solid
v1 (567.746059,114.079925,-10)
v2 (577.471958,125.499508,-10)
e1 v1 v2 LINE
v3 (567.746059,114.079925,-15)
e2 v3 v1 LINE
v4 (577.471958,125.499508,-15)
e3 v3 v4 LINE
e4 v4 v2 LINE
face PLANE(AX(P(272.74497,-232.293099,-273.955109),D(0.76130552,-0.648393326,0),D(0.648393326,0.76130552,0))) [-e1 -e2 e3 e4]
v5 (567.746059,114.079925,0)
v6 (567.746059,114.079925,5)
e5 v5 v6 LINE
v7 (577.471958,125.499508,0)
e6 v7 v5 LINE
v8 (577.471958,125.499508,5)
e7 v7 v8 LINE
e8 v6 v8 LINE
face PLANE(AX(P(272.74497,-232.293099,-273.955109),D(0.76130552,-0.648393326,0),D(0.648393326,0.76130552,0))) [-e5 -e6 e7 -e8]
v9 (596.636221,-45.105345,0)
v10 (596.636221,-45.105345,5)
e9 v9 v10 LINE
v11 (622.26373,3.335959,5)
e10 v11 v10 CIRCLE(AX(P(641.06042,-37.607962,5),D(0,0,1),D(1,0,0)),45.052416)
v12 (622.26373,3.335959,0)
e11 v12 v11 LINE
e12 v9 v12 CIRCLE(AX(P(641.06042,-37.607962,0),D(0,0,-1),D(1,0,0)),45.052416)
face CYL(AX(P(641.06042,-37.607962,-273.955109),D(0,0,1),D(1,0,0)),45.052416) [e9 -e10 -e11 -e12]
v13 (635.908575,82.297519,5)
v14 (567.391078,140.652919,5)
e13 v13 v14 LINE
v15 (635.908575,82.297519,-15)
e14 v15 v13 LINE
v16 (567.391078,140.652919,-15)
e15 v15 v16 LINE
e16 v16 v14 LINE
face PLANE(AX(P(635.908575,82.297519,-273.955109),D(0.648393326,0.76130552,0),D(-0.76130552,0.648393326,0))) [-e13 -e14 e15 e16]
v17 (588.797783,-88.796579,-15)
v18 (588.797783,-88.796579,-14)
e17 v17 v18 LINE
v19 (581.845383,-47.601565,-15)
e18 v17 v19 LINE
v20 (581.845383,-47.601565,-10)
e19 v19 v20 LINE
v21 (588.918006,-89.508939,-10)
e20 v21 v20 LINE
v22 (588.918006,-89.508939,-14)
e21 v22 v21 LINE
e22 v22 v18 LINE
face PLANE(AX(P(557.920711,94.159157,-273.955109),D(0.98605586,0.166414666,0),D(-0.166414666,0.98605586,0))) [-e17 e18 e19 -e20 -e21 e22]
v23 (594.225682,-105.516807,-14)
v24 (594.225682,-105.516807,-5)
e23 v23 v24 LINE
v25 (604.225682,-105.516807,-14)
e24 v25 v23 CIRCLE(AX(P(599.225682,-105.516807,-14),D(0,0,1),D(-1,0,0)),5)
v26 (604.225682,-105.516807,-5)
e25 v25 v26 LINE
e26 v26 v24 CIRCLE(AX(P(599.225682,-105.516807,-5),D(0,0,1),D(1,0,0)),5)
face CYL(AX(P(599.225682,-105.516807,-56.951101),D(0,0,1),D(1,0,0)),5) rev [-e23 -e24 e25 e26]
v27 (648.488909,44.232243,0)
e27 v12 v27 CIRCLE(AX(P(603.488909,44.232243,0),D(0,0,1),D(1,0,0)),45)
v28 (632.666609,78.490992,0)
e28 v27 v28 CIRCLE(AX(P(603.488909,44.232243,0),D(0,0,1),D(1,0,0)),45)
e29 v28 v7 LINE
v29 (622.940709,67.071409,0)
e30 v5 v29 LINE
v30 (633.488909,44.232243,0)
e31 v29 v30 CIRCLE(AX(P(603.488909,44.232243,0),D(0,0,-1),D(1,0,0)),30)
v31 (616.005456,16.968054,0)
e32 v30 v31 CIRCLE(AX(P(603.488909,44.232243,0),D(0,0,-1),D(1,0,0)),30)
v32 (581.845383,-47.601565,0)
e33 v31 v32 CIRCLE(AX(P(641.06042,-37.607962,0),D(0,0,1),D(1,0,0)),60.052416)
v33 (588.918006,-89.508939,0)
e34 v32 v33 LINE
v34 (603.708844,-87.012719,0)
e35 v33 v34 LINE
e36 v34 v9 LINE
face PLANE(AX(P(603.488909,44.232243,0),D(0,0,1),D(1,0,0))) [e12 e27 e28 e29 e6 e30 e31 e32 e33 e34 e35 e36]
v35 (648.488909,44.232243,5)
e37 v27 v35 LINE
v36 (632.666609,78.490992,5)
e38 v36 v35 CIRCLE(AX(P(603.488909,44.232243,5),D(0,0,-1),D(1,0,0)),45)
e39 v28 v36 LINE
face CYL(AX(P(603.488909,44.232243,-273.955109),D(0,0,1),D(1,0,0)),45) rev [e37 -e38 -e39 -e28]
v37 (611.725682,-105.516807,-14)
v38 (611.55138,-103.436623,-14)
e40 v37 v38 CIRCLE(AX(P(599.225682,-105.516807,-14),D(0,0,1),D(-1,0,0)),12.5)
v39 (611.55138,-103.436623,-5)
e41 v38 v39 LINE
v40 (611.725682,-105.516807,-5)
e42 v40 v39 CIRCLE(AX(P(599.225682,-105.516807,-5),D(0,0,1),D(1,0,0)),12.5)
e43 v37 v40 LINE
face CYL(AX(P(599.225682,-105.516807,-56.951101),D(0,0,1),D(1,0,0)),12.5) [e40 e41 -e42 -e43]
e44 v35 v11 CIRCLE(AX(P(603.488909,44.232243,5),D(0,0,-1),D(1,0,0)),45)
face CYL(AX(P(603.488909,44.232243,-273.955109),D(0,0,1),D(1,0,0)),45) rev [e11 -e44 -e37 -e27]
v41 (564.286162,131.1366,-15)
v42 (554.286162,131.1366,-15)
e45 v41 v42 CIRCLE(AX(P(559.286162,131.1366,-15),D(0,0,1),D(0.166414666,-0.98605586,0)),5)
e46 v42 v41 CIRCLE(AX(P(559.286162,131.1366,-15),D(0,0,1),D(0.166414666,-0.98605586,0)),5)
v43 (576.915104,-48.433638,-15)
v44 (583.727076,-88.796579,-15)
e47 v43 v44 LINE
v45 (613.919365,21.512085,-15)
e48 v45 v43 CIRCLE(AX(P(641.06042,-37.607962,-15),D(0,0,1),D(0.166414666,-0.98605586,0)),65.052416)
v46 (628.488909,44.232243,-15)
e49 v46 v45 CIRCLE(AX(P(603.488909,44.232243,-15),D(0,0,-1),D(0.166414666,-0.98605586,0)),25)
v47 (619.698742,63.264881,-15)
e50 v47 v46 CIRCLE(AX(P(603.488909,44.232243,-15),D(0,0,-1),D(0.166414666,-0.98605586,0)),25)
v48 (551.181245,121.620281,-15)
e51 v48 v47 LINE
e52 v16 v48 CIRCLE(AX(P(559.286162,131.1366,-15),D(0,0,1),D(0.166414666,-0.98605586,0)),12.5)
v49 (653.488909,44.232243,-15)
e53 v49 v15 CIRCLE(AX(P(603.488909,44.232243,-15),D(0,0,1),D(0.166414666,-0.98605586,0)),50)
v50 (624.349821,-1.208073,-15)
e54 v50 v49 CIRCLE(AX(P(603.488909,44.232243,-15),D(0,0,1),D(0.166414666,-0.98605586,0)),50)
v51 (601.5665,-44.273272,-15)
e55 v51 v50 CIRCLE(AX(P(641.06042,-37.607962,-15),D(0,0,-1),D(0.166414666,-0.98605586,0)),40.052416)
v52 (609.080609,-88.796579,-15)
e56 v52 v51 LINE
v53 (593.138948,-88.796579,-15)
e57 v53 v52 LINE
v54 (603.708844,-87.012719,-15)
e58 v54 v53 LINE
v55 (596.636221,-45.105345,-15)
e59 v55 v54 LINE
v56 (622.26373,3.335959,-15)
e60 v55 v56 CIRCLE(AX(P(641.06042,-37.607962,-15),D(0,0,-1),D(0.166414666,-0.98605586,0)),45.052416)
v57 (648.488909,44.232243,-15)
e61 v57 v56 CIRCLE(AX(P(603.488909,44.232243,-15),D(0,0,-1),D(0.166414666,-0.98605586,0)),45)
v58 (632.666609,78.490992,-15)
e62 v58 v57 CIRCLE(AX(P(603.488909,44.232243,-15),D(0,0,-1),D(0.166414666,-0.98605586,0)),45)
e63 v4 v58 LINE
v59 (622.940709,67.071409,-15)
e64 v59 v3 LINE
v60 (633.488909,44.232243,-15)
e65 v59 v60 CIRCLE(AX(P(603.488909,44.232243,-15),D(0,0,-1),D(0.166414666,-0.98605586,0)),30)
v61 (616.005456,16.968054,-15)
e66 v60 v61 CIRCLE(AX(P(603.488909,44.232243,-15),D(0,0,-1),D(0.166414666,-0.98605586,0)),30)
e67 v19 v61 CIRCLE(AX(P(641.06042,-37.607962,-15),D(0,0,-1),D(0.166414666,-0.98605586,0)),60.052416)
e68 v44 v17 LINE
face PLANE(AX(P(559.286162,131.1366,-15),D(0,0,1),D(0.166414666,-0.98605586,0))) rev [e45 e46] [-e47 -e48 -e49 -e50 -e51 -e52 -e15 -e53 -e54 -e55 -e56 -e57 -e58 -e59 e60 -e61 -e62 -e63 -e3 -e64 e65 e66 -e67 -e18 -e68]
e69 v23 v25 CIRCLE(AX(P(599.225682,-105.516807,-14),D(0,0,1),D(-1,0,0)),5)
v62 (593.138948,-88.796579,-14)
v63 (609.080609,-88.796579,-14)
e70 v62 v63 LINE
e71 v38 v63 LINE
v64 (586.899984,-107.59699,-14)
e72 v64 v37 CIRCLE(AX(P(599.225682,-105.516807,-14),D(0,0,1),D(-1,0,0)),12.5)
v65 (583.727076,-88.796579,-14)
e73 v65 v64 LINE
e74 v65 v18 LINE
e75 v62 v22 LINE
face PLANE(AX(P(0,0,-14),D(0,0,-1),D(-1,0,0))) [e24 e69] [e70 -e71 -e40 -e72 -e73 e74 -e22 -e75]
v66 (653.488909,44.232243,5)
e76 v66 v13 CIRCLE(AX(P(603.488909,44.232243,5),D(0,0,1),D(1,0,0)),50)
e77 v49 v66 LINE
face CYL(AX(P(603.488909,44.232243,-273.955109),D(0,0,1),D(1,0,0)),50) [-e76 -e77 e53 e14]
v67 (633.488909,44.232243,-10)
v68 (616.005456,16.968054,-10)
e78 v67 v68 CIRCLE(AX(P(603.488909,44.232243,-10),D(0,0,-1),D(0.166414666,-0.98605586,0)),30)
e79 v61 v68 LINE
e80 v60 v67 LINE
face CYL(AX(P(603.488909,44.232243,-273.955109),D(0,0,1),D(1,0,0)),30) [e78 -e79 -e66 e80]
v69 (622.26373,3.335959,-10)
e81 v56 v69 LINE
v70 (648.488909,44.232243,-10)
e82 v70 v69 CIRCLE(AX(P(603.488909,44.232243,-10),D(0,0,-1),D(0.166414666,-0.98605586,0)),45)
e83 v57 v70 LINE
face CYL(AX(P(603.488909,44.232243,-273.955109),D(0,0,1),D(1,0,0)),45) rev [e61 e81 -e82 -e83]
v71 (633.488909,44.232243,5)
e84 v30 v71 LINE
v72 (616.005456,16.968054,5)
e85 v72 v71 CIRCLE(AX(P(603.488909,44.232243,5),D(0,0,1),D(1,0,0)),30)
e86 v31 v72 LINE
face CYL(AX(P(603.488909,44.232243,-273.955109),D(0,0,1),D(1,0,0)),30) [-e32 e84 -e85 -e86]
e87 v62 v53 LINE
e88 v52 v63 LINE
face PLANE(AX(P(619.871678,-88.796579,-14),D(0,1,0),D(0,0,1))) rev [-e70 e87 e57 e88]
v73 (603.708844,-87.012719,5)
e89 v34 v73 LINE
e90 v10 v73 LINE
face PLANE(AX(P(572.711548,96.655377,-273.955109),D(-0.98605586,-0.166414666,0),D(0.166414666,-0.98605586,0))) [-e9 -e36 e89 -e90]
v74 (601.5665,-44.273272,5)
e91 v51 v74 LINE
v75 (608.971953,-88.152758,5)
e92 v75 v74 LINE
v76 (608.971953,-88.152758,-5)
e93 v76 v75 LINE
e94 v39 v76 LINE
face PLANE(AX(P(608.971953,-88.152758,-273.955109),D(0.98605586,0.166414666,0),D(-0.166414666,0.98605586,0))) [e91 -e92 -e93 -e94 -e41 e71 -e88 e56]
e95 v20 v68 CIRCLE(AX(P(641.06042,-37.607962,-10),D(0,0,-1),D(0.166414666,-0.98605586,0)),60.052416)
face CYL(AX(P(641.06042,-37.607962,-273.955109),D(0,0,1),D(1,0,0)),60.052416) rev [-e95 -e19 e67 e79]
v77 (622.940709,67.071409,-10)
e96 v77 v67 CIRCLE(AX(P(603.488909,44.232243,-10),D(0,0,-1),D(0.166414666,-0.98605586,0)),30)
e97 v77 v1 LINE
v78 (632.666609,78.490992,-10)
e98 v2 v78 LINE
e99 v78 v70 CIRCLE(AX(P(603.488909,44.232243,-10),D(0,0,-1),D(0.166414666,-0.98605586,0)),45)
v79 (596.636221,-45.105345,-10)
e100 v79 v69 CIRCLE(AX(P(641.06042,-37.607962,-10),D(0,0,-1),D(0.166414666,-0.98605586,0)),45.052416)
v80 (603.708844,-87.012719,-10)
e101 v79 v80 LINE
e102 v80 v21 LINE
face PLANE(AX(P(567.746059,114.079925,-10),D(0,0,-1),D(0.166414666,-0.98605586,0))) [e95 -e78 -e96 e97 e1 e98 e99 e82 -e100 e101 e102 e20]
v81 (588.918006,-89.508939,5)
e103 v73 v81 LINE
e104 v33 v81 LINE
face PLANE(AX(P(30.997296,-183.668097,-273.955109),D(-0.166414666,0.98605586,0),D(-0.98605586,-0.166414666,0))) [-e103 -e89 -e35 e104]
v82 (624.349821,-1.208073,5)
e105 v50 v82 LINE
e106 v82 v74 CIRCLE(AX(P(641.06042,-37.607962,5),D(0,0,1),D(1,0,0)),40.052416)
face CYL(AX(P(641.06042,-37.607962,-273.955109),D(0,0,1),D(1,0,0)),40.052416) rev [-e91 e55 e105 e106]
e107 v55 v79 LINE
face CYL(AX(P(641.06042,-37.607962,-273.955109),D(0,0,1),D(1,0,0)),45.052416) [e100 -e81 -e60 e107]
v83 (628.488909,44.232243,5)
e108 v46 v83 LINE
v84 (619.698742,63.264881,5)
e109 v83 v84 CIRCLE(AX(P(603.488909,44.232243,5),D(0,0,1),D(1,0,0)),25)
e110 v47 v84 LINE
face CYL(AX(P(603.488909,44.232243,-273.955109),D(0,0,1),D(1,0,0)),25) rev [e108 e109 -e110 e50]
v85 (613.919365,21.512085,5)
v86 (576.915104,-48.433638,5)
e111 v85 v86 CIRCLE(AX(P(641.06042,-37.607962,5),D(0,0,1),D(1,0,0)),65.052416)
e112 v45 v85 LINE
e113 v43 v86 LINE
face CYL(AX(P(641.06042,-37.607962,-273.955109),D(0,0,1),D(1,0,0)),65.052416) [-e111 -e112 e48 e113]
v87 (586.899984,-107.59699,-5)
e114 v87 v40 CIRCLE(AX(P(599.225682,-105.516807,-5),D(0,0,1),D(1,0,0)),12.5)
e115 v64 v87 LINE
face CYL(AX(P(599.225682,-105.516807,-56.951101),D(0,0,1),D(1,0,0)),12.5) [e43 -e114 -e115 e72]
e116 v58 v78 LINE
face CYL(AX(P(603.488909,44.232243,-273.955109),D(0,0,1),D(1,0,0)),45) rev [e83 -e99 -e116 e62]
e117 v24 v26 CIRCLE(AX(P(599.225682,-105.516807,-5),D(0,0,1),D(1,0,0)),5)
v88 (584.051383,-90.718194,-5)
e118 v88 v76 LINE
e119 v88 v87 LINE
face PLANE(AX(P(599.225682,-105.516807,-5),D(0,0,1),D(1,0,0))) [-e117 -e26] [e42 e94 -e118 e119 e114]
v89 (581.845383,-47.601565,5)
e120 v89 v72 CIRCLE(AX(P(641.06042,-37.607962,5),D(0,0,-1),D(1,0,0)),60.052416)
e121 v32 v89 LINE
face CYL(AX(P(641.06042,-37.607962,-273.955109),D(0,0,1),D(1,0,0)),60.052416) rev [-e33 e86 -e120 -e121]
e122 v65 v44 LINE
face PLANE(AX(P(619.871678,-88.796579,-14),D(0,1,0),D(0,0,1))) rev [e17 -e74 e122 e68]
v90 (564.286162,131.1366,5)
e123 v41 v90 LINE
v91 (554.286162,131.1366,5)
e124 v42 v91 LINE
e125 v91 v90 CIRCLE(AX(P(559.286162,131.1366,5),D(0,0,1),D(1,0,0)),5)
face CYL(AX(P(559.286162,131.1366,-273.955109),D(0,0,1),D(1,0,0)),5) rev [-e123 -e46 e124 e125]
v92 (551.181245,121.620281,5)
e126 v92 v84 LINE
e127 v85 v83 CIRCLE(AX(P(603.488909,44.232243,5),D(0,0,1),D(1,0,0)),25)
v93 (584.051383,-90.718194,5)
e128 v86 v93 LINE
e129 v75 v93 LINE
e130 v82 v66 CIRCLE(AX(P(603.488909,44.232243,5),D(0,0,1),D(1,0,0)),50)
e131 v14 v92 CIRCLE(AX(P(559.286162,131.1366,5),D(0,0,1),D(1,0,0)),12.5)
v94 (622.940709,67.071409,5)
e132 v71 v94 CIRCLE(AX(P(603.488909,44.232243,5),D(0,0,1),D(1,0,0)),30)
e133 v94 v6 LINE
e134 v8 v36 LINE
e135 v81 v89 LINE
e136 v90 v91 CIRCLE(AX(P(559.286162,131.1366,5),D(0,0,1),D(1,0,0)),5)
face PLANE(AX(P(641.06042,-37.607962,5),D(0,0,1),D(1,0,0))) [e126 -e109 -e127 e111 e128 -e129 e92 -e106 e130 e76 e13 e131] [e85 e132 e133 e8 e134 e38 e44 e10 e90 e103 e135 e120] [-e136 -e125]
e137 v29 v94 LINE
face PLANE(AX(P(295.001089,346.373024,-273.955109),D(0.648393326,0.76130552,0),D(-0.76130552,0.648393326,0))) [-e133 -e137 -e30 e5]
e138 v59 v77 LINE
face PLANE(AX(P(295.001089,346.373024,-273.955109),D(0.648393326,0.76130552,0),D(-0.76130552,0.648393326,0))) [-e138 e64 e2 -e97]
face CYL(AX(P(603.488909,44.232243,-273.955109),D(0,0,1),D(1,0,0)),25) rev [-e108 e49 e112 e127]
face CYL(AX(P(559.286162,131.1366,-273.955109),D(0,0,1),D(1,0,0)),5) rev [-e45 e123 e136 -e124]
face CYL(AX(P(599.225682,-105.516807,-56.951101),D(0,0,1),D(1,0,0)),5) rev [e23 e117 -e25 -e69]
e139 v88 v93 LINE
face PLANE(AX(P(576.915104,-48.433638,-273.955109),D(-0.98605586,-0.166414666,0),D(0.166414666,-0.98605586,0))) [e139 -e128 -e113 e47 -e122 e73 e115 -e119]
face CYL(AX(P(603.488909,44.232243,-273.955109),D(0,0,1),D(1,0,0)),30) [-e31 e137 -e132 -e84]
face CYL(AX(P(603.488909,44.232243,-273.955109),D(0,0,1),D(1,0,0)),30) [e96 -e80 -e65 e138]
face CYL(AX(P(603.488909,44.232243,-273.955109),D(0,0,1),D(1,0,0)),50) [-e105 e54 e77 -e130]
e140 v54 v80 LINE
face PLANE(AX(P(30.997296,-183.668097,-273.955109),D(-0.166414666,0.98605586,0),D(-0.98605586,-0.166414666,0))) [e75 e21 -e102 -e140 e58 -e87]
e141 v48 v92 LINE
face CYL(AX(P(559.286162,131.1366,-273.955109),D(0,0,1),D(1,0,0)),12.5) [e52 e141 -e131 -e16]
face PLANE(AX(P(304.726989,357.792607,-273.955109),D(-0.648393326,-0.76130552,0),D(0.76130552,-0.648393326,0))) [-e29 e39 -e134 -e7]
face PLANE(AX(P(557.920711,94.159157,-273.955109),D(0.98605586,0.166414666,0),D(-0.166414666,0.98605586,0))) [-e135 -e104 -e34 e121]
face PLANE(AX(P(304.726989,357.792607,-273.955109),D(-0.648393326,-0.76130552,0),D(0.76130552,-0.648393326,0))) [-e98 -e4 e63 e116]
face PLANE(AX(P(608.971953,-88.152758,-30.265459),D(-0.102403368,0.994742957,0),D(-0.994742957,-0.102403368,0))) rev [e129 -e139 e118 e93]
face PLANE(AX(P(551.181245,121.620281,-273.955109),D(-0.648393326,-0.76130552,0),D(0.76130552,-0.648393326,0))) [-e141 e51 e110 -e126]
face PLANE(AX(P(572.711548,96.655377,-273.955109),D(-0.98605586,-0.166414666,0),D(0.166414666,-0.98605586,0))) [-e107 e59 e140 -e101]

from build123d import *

# Parameters (mm, degrees)
BOSS_EXTRUDE1_DEPTH = 10
BOSS_EXTRUDE2_START = -20
BOSS_EXTRUDE2_DEPTH = 20
BOSS_EXTRUDE3_DEPTH = 10
SKETCH6_W           = 47.967212756
SKETCH6_H           = 31.917124467
CUT_EXTRUDE1_DEPTH  = 1
CUT_EXTRUDE2_DEPTH  = 10


with BuildPart() as part:
    # Sketch2 → Boss-Extrude1 (new body)
    with BuildSketch(Plane.XY):
        with BuildLine():
            Line((567.746058529, 114.079925051), (622.940708708, 67.071408889))
            ThreePointArc((622.940708708, 67.071408889), (633.205576943, 40.118894124), (616.005456238, 16.96805354))
            ThreePointArc((616.005456238, 16.96805354), (587.978717163, -9.525484834), (581.845382902, -47.601565115))
            Line((581.845382902, -47.601565115), (588.918006227, -89.508939159))
            Line((588.918006227, -89.508939159), (603.708844125, -87.012719162))
            Line((603.708844125, -87.012719162), (596.6362208, -45.105345118))
            ThreePointArc((596.6362208, -45.105345118), (601.237559856, -16.539976295), (622.263729898, 3.335958661))
            ThreePointArc((622.263729898, 3.335958661), (648.063910956, 38.062219537), (632.666608603, 78.490991685))
            Line((632.666608603, 78.490991685), (577.471958425, 125.499507846))
            Line((577.471958425, 125.499507846), (567.746058529, 114.079925051))
        make_face()
    extrude(amount=-BOSS_EXTRUDE1_DEPTH)

    # Sketch3 → Boss-Extrude2 (add)
    with BuildSketch(Plane.XY.offset(5).offset(BOSS_EXTRUDE2_START)):
        with BuildLine():
            Line((608.971952758, -88.152757549), (601.566500099, -44.273271785))
            ThreePointArc((601.566500099, -44.273271785), (605.657174086, -18.878140116), (624.349821118, -1.208072965))
            ThreePointArc((624.349821118, -1.208072965), (653.01668896, 37.376661342), (635.908575235, 82.297519283))
            Line((635.908575235, 82.297519283), (567.391078462, 140.652918656))
            ThreePointArc((567.391078462, 140.652918656), (549.769842886, 139.241516239), (551.181245303, 121.620280664))
            Line((551.181245303, 121.620280664), (619.698742076, 63.264881291))
            ThreePointArc((619.698742076, 63.264881291), (628.252798938, 40.80445232), (613.919365017, 21.512085166))
            ThreePointArc((613.919365017, 21.512085166), (583.559102933, -7.187321014), (576.915103602, -48.433638447))
            Line((576.915103602, -48.433638447), (584.320556261, -92.313124211))
            Line((584.320556261, -92.313124211), (608.971952758, -88.152757549))
        make_face()
        with BuildLine():
            Line((577.471958425, 125.499507846), (567.746058529, 114.079925051))
            Line((567.746058529, 114.079925051), (622.940708708, 67.071408889))
            ThreePointArc((622.940708708, 67.071408889), (633.205576943, 40.118894124), (616.005456238, 16.96805354))
            ThreePointArc((616.005456238, 16.96805354), (587.978717163, -9.525484834), (581.845382902, -47.601565115))
            Line((581.845382902, -47.601565115), (588.918006227, -89.508939159))
            Line((588.918006227, -89.508939159), (603.708844125, -87.012719162))
            Line((603.708844125, -87.012719162), (596.6362208, -45.105345118))
            ThreePointArc((596.6362208, -45.105345118), (601.237559856, -16.539976295), (622.263729898, 3.335958661))
            ThreePointArc((622.263729898, 3.335958661), (648.063910956, 38.062219537), (632.666608603, 78.490991685))
            Line((632.666608603, 78.490991685), (577.471958425, 125.499507846))
        make_face(mode=Mode.SUBTRACT)
        with BuildLine():
            ThreePointArc((558.45408855, 136.066878959), (554.355882583, 130.304526327), (560.118235215, 126.20632036))
            ThreePointArc((560.118235215, 126.20632036), (564.216441182, 131.968672992), (558.45408855, 136.066878959))
        make_face(mode=Mode.SUBTRACT)
    extrude(amount=BOSS_EXTRUDE2_DEPTH)

    # Sketch4 → Boss-Extrude3 (add)
    with BuildSketch(Plane.XY.offset(-5)):
        with BuildLine():
            Line((608.696660412, -86.521569404), (584.013862627, -90.495874195))
            Line((584.013862627, -90.495874195), (586.899983592, -107.596990039))
            ThreePointArc((586.899983592, -107.596990039), (601.305865171, -117.842504957), (611.551380088, -103.436623377))
            Line((611.551380088, -103.436623377), (608.696660412, -86.521569404))
        make_face()
        with BuildLine():
            ThreePointArc((598.393608507, -100.586527409), (594.295402541, -106.348880041), (600.057755172, -110.447086008))
            ThreePointArc((600.057755172, -110.447086008), (604.155961139, -104.684733376), (598.393608507, -100.586527409))
        make_face(mode=Mode.SUBTRACT)
    extrude(amount=-BOSS_EXTRUDE3_DEPTH)

    # Sketch6 → Cut-Extrude1 (cut)
    with BuildSketch(Plane(origin=(0, 0, -15), x_dir=(-1, 0, 0), z_dir=(0, 0, -1))):
        with Locations((-595.88807181, -104.755141446)):
            Rectangle(SKETCH6_W, SKETCH6_H)
    extrude(amount=-CUT_EXTRUDE1_DEPTH, mode=Mode.SUBTRACT)

    # Sketch7 → Cut-Extrude2 (cut)
    with BuildSketch(Plane.XY.offset(5)):
        Polygon((608.971952758, -88.152757549), (584.051383166, -90.718194429), (584.320556261, -92.313124211), align=None)
    extrude(amount=-CUT_EXTRUDE2_DEPTH, mode=Mode.SUBTRACT)


solid = part.part
